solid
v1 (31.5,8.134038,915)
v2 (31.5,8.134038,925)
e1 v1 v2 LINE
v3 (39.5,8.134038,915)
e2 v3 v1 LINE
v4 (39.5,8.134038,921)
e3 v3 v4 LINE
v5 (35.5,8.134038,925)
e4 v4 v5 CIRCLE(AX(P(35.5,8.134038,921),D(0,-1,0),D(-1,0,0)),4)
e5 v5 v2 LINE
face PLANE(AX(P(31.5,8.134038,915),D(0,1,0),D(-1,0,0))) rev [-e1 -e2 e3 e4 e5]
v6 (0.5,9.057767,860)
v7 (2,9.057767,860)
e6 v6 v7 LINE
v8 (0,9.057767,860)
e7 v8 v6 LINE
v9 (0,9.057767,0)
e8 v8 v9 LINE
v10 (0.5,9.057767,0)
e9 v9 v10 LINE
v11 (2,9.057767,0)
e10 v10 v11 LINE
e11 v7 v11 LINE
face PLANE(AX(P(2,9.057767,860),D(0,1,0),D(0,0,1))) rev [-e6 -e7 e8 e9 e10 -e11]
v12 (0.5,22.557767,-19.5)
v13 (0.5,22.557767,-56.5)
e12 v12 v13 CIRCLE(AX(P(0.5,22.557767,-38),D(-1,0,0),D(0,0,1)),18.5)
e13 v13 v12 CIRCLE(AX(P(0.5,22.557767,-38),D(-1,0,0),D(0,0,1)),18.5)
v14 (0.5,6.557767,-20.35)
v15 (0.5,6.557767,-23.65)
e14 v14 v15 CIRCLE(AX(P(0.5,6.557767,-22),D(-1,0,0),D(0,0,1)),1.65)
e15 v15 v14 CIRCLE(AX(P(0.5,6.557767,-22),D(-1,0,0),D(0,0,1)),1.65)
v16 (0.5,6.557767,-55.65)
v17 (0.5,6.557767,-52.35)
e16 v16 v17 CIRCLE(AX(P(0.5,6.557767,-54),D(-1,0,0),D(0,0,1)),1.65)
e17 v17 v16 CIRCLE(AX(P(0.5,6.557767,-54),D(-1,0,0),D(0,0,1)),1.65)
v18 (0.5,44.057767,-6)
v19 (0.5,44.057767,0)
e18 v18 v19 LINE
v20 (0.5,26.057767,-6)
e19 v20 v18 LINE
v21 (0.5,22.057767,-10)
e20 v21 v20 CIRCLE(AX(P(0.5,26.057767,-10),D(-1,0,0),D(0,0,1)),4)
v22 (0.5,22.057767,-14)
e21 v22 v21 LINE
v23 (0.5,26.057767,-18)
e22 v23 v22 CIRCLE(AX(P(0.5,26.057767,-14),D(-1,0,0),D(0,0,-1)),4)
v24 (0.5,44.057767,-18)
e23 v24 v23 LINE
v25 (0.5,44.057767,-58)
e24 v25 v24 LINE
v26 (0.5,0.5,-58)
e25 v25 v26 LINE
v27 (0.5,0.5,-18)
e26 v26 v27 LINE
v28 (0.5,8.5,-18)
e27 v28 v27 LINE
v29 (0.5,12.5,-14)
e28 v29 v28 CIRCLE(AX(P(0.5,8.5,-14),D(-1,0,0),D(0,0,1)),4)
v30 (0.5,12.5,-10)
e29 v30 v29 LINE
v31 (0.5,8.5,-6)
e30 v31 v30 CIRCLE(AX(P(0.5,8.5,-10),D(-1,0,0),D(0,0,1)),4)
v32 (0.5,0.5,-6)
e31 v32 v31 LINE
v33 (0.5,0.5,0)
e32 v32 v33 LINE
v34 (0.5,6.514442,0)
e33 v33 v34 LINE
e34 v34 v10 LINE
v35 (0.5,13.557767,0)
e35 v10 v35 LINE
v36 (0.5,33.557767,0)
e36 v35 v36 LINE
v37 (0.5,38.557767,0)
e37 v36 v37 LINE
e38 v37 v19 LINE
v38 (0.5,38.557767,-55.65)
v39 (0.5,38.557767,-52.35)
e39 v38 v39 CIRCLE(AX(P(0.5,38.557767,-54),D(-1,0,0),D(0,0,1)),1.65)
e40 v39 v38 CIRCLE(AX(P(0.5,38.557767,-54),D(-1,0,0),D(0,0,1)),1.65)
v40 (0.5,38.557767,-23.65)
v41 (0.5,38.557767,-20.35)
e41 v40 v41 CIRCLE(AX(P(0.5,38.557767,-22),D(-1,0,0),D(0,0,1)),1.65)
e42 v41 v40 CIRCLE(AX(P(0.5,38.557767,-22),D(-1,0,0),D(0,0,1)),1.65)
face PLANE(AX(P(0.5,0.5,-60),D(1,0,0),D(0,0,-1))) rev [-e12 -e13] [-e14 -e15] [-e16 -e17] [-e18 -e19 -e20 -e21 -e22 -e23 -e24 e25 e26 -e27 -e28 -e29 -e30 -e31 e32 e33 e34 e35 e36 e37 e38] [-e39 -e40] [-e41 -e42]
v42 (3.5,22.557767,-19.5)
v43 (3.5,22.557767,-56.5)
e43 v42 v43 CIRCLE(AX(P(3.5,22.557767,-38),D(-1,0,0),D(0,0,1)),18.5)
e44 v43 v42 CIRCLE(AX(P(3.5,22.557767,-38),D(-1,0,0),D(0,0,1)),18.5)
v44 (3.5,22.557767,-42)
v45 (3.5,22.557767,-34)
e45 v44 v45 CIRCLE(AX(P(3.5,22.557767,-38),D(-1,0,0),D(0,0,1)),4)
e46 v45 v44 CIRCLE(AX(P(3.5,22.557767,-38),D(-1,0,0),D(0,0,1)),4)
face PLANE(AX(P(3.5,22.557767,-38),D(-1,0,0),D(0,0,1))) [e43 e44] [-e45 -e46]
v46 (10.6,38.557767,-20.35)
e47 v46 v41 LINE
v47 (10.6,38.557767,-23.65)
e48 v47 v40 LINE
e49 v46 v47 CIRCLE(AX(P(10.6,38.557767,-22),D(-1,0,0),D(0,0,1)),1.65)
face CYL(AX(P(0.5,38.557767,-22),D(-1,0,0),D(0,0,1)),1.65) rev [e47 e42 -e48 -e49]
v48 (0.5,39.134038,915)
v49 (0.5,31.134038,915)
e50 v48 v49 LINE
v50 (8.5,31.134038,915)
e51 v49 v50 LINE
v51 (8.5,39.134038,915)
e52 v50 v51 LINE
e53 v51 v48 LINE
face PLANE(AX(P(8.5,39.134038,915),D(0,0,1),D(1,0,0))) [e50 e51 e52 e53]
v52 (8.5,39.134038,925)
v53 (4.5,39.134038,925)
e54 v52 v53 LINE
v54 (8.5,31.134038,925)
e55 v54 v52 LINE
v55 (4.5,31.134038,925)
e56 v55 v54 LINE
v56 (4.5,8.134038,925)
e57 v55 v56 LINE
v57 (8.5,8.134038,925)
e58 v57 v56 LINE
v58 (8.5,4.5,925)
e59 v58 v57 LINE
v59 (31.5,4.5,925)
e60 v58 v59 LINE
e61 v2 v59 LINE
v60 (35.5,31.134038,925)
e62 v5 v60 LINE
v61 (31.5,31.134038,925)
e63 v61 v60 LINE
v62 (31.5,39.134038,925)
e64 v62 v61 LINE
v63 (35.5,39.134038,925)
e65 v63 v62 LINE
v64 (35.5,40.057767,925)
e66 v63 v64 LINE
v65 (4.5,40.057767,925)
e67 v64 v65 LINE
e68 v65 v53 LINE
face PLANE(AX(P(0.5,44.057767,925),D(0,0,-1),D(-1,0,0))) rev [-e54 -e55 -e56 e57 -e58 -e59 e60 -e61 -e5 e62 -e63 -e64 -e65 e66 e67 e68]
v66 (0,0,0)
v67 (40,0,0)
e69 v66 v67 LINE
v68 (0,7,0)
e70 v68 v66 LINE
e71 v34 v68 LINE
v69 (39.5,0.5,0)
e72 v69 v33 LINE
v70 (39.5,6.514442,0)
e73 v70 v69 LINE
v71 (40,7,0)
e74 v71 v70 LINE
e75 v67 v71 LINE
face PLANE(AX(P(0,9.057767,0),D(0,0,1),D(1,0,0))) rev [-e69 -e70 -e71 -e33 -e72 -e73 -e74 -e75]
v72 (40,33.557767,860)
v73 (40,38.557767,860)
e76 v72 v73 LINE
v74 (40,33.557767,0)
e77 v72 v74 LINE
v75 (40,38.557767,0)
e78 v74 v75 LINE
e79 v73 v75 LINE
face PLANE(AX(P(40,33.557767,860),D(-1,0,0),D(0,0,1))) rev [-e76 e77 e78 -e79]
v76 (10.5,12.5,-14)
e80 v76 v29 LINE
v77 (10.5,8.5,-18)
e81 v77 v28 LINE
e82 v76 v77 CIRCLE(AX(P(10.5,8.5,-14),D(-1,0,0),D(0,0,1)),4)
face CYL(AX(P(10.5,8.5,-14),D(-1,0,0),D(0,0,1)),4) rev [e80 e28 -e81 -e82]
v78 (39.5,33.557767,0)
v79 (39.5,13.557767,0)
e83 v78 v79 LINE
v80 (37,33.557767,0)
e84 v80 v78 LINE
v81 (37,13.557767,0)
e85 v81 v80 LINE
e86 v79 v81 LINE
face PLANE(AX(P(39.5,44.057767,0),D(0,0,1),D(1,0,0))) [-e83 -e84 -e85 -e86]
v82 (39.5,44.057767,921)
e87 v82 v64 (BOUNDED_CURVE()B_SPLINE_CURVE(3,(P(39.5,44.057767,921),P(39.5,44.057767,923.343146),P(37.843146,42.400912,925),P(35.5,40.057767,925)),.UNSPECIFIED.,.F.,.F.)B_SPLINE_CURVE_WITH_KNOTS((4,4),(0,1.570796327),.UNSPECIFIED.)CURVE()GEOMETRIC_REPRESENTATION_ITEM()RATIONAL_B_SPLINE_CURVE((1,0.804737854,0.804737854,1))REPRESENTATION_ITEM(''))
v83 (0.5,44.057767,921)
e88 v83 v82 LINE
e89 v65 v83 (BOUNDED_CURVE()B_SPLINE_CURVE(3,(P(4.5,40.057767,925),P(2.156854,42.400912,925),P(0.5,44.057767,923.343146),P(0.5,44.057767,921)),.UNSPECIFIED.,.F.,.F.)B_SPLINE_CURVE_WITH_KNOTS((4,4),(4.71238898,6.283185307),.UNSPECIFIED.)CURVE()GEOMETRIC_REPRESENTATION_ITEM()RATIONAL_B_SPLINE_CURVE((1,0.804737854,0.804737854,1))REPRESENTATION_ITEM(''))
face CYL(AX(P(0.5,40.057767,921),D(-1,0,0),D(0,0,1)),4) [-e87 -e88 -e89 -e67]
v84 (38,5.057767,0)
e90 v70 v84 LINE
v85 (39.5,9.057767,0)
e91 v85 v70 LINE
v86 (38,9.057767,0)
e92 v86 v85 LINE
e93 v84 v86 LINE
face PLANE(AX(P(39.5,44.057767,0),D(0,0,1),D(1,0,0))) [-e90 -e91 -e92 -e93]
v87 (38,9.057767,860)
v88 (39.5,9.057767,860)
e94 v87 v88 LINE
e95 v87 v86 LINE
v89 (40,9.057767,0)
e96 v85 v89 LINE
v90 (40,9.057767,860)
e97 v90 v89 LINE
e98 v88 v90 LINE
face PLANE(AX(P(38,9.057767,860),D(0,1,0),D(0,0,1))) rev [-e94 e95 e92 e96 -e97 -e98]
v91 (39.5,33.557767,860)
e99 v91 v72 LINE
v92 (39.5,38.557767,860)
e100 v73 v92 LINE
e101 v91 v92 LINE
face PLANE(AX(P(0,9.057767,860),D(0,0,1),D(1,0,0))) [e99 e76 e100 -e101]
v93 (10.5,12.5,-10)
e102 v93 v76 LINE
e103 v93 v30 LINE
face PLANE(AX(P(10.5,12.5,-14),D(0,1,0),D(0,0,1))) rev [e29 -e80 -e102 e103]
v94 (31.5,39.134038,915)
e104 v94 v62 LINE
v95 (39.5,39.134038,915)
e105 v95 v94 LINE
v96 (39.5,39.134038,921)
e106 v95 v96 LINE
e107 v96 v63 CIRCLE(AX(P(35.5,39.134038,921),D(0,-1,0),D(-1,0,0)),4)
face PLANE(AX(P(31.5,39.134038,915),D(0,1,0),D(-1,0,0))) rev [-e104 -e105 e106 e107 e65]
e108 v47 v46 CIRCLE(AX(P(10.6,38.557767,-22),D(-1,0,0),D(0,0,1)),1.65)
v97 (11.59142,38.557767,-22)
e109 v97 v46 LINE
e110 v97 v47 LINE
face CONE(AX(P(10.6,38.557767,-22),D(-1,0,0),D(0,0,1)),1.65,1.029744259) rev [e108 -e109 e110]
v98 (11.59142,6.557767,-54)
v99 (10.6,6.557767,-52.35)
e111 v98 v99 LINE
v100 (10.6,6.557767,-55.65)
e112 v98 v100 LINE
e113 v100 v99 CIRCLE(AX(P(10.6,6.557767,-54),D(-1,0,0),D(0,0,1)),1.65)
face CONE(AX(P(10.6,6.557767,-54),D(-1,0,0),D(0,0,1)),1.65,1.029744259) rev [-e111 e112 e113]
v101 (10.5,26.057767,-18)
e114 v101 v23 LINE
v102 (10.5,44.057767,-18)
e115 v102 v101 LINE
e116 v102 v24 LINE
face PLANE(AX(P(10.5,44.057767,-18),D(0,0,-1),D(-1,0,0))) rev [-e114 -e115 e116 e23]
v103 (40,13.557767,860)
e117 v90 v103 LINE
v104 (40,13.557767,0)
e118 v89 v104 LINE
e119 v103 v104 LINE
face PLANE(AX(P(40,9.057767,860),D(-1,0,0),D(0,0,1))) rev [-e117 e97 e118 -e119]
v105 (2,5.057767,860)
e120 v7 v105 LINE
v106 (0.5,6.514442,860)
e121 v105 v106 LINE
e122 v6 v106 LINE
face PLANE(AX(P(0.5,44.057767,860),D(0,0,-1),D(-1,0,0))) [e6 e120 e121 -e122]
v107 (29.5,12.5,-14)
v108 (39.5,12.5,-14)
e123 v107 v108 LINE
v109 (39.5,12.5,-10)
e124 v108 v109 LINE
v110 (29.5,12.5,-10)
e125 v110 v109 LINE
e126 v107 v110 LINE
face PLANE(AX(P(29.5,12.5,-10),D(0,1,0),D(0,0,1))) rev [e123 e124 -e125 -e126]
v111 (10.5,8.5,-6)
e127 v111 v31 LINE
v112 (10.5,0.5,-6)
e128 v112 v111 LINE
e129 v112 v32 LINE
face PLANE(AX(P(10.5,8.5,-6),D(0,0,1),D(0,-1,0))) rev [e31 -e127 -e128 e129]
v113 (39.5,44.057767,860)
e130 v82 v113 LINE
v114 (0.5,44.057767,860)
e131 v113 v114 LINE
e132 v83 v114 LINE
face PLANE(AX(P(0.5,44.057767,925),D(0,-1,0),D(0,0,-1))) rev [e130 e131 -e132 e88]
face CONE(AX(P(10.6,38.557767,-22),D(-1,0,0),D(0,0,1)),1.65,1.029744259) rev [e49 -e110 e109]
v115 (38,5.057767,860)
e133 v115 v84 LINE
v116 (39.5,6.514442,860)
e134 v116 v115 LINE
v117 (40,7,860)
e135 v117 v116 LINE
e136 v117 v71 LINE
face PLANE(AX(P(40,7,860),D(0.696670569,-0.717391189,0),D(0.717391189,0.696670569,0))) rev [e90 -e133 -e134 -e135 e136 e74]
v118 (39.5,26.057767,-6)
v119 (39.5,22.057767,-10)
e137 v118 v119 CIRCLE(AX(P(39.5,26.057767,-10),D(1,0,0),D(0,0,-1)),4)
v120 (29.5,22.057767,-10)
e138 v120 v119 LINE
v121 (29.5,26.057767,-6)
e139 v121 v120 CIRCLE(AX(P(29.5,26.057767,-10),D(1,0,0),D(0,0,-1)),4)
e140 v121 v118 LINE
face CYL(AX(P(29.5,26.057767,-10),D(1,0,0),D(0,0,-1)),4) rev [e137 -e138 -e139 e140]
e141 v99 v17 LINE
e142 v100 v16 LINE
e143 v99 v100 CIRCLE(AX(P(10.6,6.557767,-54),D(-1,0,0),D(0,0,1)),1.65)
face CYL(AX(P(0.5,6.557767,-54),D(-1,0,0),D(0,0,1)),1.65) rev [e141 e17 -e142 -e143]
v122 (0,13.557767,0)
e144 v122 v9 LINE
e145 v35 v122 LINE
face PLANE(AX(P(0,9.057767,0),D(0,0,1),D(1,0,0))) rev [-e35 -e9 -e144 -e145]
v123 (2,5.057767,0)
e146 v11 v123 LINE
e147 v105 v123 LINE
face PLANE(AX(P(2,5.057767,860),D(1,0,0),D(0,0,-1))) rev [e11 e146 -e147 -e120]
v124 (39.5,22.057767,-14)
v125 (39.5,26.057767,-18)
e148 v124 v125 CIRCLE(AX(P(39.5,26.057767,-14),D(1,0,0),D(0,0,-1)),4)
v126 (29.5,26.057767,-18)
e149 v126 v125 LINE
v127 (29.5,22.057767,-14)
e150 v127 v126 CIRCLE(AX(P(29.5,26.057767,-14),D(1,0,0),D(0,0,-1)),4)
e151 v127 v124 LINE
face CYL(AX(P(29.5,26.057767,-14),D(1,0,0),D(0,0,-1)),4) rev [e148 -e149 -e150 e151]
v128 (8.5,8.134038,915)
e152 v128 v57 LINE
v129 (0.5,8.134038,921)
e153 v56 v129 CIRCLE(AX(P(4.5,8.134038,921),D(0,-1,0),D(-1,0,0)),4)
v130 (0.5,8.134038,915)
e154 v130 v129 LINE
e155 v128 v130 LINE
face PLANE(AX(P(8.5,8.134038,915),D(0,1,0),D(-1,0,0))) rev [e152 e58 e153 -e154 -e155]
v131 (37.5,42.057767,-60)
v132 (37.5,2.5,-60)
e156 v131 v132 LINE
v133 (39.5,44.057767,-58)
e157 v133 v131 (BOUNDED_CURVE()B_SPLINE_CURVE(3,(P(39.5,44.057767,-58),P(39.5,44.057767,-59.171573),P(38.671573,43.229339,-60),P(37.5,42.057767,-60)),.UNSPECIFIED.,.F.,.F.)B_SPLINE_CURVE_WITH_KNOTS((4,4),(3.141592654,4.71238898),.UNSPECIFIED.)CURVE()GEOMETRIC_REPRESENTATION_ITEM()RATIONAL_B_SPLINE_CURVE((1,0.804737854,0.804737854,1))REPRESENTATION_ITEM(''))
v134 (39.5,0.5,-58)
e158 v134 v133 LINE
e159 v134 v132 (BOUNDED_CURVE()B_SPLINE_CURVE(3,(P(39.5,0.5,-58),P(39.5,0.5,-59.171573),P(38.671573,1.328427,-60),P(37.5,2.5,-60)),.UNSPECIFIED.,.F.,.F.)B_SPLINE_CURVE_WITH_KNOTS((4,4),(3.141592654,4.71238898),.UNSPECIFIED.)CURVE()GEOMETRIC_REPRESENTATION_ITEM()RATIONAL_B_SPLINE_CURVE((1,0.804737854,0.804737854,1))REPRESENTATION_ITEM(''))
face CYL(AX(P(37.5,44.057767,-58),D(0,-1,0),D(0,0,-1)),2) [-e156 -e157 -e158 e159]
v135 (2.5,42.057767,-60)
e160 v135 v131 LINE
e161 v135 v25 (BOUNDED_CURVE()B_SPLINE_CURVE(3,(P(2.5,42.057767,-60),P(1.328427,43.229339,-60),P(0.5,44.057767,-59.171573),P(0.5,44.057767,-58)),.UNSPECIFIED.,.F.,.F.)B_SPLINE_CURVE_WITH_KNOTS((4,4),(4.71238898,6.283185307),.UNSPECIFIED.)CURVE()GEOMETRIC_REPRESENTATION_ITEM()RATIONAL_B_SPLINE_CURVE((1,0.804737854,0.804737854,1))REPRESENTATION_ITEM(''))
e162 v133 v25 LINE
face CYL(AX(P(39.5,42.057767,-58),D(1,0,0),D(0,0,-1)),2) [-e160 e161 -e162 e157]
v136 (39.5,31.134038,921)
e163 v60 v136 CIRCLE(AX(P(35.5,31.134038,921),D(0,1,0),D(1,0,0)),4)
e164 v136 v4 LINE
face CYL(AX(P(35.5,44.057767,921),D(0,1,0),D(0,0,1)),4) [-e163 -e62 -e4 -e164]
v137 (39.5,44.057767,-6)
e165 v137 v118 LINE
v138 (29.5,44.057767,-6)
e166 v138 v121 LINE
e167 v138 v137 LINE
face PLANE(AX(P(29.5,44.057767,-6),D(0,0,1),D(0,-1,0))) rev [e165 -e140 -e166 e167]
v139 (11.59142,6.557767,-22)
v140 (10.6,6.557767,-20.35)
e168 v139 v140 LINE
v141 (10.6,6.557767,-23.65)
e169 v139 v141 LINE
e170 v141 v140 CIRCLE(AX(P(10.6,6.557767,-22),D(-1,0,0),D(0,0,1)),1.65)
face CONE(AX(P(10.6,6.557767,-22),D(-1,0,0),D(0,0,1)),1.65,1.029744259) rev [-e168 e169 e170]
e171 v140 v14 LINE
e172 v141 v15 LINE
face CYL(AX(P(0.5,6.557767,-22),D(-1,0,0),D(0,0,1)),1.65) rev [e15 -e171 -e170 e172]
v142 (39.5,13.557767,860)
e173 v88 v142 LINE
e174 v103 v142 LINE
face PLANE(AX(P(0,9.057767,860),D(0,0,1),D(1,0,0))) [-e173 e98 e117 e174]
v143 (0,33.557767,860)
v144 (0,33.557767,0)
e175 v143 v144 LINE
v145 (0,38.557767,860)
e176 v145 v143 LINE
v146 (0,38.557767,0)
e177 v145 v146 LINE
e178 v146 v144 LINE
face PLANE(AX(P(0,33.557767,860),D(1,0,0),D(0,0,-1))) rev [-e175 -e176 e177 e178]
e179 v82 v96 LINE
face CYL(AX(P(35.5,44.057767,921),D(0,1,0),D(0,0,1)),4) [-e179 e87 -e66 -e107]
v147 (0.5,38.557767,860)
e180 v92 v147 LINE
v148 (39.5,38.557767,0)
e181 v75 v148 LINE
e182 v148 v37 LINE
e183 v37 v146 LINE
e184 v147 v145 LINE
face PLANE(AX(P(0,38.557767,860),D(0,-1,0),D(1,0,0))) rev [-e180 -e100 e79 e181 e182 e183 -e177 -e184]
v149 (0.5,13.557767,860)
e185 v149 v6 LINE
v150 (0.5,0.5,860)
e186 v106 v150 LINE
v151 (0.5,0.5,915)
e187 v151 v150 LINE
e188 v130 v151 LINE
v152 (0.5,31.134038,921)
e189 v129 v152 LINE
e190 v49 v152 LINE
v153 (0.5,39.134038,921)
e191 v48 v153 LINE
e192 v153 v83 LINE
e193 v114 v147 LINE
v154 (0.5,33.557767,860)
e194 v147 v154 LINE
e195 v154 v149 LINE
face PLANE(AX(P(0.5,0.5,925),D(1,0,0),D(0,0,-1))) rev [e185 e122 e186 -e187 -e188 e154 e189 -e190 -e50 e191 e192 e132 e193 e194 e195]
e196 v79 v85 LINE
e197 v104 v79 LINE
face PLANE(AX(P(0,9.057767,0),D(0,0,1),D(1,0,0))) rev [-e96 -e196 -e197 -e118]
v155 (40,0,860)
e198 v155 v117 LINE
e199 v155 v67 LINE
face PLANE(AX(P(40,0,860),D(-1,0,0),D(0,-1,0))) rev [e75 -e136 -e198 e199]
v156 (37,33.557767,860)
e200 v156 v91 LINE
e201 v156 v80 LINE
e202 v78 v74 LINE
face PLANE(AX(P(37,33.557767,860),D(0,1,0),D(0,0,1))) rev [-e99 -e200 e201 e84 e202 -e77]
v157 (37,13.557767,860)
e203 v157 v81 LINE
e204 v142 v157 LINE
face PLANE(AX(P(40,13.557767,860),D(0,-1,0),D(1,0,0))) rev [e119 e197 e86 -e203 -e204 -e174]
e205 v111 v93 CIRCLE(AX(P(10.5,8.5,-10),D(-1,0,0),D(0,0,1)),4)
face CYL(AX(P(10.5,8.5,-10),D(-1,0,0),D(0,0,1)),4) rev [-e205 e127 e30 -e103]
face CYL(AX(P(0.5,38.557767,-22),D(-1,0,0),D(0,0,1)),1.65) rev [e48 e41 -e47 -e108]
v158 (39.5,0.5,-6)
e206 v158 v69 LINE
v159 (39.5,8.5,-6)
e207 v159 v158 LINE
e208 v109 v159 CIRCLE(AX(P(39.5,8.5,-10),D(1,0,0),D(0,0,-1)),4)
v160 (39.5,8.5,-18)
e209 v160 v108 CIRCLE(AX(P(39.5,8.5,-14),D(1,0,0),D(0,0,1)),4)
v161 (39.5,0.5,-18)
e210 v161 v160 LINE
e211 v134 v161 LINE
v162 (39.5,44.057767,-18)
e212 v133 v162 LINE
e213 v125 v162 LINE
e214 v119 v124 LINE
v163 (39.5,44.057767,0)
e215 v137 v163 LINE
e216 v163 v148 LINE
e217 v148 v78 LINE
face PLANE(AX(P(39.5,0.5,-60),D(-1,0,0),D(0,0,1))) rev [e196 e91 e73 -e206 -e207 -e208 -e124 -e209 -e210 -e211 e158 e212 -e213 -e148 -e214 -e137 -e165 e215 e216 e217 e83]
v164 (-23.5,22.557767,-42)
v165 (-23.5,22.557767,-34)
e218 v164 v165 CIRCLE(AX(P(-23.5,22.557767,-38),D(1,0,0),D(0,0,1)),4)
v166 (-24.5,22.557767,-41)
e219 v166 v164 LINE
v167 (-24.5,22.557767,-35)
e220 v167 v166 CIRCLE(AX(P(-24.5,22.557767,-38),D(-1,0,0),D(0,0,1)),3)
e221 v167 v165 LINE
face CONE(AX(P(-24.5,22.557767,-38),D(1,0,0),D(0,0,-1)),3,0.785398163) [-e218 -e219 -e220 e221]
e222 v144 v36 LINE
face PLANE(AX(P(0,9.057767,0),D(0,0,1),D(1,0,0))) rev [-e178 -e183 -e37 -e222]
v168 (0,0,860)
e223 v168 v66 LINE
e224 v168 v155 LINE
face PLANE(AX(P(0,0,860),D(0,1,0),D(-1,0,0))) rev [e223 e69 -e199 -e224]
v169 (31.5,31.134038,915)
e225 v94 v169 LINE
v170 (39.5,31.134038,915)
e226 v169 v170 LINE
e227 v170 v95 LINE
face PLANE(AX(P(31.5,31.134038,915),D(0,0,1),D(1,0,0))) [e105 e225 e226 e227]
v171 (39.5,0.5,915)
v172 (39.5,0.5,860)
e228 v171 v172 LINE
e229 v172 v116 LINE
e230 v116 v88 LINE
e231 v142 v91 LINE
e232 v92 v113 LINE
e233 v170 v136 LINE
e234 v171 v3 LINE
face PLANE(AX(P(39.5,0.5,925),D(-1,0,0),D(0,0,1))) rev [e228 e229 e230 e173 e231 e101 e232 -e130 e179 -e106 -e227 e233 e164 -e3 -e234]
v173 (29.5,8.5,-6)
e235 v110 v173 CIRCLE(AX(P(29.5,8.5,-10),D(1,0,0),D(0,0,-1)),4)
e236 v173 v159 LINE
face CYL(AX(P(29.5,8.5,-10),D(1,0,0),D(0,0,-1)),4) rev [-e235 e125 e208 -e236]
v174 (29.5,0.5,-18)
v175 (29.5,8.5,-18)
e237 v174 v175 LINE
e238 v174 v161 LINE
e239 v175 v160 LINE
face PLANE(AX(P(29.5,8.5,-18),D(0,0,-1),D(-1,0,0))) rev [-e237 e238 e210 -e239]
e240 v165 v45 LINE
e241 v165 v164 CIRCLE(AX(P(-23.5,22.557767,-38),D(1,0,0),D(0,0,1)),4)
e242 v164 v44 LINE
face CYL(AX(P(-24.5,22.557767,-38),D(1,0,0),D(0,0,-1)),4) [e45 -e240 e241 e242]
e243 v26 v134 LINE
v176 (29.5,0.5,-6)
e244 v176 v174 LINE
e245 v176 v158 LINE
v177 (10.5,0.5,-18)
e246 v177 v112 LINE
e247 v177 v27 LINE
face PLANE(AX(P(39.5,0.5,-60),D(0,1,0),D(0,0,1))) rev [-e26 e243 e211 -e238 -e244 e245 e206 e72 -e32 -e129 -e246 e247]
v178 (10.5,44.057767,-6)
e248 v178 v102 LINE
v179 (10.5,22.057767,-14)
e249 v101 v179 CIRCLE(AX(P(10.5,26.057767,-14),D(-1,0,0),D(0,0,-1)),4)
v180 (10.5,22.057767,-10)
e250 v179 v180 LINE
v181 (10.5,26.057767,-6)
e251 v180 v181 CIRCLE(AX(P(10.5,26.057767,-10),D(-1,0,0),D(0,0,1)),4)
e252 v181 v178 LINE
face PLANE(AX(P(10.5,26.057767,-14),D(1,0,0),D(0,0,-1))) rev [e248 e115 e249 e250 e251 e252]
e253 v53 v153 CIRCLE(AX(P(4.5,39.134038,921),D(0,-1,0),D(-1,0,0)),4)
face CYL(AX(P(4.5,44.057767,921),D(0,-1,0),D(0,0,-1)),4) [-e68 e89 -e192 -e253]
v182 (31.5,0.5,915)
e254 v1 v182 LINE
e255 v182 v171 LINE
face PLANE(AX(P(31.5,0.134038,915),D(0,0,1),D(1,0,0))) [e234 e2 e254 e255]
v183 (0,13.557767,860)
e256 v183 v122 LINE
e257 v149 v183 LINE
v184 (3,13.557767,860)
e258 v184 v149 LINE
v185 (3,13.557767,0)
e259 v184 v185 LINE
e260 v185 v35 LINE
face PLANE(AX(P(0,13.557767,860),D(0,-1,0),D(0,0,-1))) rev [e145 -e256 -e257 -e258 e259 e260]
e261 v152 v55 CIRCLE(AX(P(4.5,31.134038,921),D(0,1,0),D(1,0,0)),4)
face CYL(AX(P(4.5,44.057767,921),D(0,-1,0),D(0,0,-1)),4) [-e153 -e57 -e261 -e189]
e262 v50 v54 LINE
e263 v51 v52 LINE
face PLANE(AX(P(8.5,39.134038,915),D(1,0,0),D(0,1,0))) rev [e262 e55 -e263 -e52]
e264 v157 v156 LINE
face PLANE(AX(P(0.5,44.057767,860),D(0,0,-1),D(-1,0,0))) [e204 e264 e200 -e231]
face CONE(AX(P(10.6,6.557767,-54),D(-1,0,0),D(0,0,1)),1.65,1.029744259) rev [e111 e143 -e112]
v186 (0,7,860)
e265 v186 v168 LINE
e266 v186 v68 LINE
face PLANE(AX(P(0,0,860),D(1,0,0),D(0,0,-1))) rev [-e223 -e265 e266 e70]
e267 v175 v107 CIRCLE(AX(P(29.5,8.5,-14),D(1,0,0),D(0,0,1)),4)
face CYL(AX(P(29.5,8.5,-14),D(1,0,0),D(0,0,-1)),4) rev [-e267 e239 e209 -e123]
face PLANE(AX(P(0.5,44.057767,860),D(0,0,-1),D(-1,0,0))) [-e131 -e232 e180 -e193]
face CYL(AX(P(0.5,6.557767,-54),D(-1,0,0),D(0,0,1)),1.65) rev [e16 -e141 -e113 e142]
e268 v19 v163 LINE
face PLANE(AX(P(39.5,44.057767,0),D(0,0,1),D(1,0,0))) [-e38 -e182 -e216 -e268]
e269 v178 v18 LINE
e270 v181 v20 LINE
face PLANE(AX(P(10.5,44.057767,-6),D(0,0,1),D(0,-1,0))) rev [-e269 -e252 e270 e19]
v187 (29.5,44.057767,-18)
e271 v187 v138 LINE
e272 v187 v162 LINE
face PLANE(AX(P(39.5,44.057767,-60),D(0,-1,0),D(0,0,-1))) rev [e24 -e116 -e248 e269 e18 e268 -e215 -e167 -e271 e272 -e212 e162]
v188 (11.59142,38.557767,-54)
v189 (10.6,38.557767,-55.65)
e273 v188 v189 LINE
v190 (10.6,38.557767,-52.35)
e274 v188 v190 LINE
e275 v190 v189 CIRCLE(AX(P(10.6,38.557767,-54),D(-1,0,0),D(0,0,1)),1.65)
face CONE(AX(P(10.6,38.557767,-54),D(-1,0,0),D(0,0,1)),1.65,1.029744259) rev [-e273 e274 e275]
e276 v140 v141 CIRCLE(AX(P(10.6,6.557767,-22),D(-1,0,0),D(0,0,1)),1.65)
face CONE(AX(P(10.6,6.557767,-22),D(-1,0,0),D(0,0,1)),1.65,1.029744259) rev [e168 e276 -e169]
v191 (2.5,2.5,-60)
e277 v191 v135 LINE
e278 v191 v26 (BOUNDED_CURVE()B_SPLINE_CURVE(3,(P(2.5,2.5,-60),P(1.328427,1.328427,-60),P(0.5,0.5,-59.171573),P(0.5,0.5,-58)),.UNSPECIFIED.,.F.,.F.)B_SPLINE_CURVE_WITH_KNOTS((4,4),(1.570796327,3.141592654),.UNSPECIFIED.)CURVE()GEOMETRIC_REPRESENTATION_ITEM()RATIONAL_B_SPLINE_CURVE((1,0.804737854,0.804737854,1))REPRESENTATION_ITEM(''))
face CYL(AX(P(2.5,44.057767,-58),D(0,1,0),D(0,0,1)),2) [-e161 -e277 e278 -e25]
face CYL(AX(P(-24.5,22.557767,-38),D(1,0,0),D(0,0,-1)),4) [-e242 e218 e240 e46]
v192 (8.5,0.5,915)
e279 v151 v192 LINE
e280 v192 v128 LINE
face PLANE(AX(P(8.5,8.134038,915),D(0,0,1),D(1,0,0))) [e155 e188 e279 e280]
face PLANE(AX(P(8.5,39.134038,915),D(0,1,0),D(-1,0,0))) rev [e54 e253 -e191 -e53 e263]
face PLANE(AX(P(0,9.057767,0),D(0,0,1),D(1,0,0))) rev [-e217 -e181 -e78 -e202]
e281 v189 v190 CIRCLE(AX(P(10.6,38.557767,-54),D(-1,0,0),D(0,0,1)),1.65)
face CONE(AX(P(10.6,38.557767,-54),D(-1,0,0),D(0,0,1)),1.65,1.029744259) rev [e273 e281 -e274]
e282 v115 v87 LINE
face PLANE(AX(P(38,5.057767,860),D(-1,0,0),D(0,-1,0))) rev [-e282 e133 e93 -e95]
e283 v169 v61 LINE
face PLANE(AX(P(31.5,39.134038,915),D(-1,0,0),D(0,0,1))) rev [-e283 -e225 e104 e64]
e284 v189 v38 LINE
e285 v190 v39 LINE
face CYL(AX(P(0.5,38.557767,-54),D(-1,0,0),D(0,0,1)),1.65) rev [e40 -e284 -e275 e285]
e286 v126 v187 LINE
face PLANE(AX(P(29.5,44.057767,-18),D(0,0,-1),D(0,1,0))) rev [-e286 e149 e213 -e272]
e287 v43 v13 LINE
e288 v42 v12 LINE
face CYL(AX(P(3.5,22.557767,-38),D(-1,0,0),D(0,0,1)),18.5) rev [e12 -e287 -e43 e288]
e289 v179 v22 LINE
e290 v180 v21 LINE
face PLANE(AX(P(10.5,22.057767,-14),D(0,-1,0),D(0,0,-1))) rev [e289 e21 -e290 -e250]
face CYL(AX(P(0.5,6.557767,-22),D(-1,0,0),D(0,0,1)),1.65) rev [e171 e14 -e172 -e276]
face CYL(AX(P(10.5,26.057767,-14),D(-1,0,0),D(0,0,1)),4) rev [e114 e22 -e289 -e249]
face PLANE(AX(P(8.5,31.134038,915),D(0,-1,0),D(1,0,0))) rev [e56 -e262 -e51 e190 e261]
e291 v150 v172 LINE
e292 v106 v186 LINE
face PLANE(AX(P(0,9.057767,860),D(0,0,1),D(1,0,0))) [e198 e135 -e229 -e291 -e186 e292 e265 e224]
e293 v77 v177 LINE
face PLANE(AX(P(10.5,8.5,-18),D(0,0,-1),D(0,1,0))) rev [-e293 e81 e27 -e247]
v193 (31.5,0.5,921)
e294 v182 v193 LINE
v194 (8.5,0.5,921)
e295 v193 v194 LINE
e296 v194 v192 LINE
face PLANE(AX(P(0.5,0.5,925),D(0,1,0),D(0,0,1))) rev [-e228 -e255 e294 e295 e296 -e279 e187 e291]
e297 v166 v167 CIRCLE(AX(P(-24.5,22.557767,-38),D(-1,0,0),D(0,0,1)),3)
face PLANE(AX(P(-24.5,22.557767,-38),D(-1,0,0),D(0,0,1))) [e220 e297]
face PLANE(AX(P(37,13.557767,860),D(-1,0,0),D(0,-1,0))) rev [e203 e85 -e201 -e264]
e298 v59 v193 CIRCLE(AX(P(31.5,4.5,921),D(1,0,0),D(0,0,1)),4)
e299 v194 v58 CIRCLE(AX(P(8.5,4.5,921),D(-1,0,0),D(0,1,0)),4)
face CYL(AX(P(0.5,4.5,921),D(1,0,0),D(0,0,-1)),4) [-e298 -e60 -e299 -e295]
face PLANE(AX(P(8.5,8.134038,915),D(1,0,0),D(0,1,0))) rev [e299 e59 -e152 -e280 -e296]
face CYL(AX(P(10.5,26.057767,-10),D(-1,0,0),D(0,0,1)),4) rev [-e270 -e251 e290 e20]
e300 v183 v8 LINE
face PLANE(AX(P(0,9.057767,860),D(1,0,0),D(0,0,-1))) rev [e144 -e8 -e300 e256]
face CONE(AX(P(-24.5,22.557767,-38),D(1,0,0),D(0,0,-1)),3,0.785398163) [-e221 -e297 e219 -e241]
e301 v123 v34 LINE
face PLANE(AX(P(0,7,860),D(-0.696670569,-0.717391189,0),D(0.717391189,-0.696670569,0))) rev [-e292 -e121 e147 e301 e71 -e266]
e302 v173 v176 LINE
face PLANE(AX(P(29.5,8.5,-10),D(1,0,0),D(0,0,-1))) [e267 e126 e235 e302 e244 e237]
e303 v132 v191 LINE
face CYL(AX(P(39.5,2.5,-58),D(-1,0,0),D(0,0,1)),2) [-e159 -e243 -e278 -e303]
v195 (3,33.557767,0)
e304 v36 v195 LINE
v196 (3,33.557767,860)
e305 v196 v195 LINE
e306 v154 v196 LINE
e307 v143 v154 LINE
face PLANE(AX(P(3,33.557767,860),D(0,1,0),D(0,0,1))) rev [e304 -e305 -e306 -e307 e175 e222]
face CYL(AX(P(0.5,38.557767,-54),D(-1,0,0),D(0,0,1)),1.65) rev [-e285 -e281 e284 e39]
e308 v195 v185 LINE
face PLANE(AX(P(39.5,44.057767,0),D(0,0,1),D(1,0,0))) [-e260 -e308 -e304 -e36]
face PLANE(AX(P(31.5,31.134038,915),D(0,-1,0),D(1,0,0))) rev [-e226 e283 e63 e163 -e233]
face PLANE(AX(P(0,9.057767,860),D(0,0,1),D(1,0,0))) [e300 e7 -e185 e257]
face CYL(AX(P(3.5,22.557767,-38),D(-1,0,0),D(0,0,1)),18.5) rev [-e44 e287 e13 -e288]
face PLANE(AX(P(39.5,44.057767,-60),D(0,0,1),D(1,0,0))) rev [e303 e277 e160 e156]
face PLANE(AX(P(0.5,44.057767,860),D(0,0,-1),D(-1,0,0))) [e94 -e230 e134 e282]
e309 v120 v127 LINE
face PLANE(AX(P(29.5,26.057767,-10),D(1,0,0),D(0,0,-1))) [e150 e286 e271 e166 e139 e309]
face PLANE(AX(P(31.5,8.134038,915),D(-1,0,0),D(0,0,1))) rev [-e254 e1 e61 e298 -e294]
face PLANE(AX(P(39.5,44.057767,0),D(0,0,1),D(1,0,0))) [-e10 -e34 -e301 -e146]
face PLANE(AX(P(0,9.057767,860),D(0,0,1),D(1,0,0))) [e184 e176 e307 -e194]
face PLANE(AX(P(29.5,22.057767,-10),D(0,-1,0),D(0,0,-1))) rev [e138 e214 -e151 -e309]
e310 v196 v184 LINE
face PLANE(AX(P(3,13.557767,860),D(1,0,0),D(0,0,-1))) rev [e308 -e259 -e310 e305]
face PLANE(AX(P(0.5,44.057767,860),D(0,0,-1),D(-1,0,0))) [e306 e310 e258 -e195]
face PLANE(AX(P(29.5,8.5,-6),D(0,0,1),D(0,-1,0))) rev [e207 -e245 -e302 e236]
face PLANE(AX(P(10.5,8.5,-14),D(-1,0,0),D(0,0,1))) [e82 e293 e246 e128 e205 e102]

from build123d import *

# Parameters (mm, degrees)
EXTRUDE_473_DEPTH      = 860
SKETCH_2_W             = 39
SKETCH_2_H             = 43.557766586
EXTRUDE_1_DEPTH        = 65
FILLET_2_R             = 4
SKETCH_3_W             = 8
SKETCH_3_H             = 8
CUT_EXTRUDE_1_DEPTH    = 10
SKETCH_4_W             = 39
SKETCH_4_H             = 43.557766586
EXTRUDE_3_DEPTH        = 60
FILLET_4_R             = 2
CUT_EXTRUDE_2_DEPTH    = 10
CUT_EXTRUDE_START      = -10
CUT_EXTRUDE_3_DEPTH    = 10
HOLE_WIZARD_M4_1_D     = 3.3
HOLE_WIZARD_M4_1_DEPTH = 10.1
HOLE_WIZARD_M4_1_TIP   = 0.991420021
SKETCH_13_R            = 18.5
CUT_EXTRUDE_4_DEPTH    = 3
SKETCH_14_R            = 4
EXTRUDE_5_DEPTH        = 28
CHAMFER_1_SIZE         = 1


with BuildPart() as part:
    # 草图1 → Extrude 473 (new body)
    with BuildSketch(Plane.XY):
        Polygon((0, 0), (40, 0), (40, 7), (38, 5.057766586), (38, 9.057766586), (40, 9.057766586), (40, 13.557766586), (37, 13.557766586), (37, 33.557766586), (40, 33.557766586), (40, 38.557766586), (0, 38.557766586), (0, 33.557766586), (3, 33.557766586), (3, 13.557766586), (0, 13.557766586), (0, 9.057766586), (2, 9.057766586), (2, 5.057766586), (0, 7), align=None)
    extrude(amount=EXTRUDE_473_DEPTH)

    # 草图2 → 凸台-拉伸1 (add)
    with BuildSketch(Plane.XY.offset(860)):
        with Locations((20, 22.278883293)):
            Rectangle(SKETCH_2_W, SKETCH_2_H)
    extrude(amount=EXTRUDE_1_DEPTH)

    # 圆角2
    fillet_2_edges = [part.edges().sort_by_distance(p)[0] for p in [
        (0.5, 22.278883293, 925),
        (20, 0.5, 925),
        (39.5, 22.278883293, 925),
        (20, 44.057766586, 925),
    ]]
    fillet(fillet_2_edges, radius=FILLET_2_R)

    # 草图3 → 切除-拉伸1 (cut)
    with BuildSketch(Plane.XY.offset(925)):
        with Locations((4.5, 35.134037638)):
            Rectangle(SKETCH_3_W, SKETCH_3_H)
        with Locations((35.5, 4.134037638)):
            Rectangle(SKETCH_3_W, SKETCH_3_H)
        with Locations((35.5, 35.134037638)):
            Rectangle(SKETCH_3_W, SKETCH_3_H)
        with Locations((4.5, 4.134037638)):
            Rectangle(SKETCH_3_W, SKETCH_3_H)
    extrude(amount=-CUT_EXTRUDE_1_DEPTH, mode=Mode.SUBTRACT)

    # 草图4 → 凸台-拉伸3 (add)
    with BuildSketch(Plane(origin=(0, 0, 0), x_dir=(-1, 0, 0), z_dir=(0, 0, -1))):
        with Locations((-20, 22.278883293)):
            Rectangle(SKETCH_4_W, SKETCH_4_H)
    extrude(amount=EXTRUDE_3_DEPTH)

    # 圆角4
    fillet_4_edges = [part.edges().sort_by_distance(p)[0] for p in [
        (39.5, 22.278883293, -60),
        (20, 0.5, -60),
        (0.5, 22.278883293, -60),
        (20, 44.057766586, -60),
    ]]
    fillet(fillet_4_edges, radius=FILLET_4_R)

    # 草图5 → 切除-拉伸2 (cut)
    with BuildSketch(Plane.ZY.offset(-0.5)):
        with BuildLine():
            Line((-18, 44.057766586), (-6, 44.057766586))
            Line((-6, 44.057766586), (-6, 26.057766586))
            ThreePointArc((-6, 26.057766586), (-7.171572875, 23.229339461), (-10, 22.057766586))
            Line((-10, 22.057766586), (-14, 22.057766586))
            ThreePointArc((-14, 22.057766586), (-16.828427125, 23.229339461), (-18, 26.057766586))
            Line((-18, 26.057766586), (-18, 44.057766586))
        make_face()
        with BuildLine():
            Line((-14, 12.5), (-10, 12.5))
            ThreePointArc((-10, 12.5), (-7.171572875, 11.328427125), (-6, 8.5))
            Line((-6, 8.5), (-6, 0.5))
            Line((-6, 0.5), (-18, 0.5))
            Line((-18, 0.5), (-18, 8.5))
            ThreePointArc((-18, 8.5), (-16.828427125, 11.328427125), (-14, 12.5))
        make_face()
    extrude(amount=-CUT_EXTRUDE_2_DEPTH, mode=Mode.SUBTRACT)

    # 草图7 → 切除-拉伸3 (cut)
    with BuildSketch(Plane(origin=(39.5, 0, 0), x_dir=(0, 0, -1), z_dir=(1, 0, 0)).offset(CUT_EXTRUDE_START)):
        with BuildLine():
            Line((6, 44.057766586), (18, 44.057766586))
            Line((18, 44.057766586), (18, 26.057766586))
            ThreePointArc((18, 26.057766586), (16.828427125, 23.229339461), (14, 22.057766586))
            Line((14, 22.057766586), (10, 22.057766586))
            ThreePointArc((10, 22.057766586), (7.171572875, 23.229339461), (6, 26.057766586))
            Line((6, 26.057766586), (6, 44.057766586))
        make_face()
        with BuildLine():
            Line((10, 12.5), (14, 12.5))
            ThreePointArc((14, 12.5), (16.828427125, 11.328427125), (18, 8.5))
            Line((18, 8.5), (18, 0.5))
            Line((18, 0.5), (6, 0.5))
            Line((6, 0.5), (6, 8.5))
            ThreePointArc((6, 8.5), (7.171572875, 11.328427125), (10, 12.5))
        make_face()
    extrude(amount=CUT_EXTRUDE_3_DEPTH, mode=Mode.SUBTRACT)

    # M4 螺纹孔1
    with Locations(Plane.ZY.offset(-0.5)):
        with Locations((-22, 6.557766586), (-54, 6.557766586), (-22, 38.557766586), (-54, 38.557766586)):
            Hole(HOLE_WIZARD_M4_1_D / 2, depth=HOLE_WIZARD_M4_1_DEPTH)
            with Locations((0, 0, -(HOLE_WIZARD_M4_1_DEPTH + HOLE_WIZARD_M4_1_TIP / 2))):  # 118° drill point
                Cone(0, HOLE_WIZARD_M4_1_D / 2, HOLE_WIZARD_M4_1_TIP, mode=Mode.SUBTRACT)

    # 草图13 → 切除-拉伸4 (cut)
    with BuildSketch(Plane.ZY.offset(-0.5)):
        with Locations((-38, 22.557766586)):
            Circle(SKETCH_13_R)
    extrude(amount=-CUT_EXTRUDE_4_DEPTH, mode=Mode.SUBTRACT)

    # 草图14 → 凸台-拉伸5 (add)
    with BuildSketch(Plane.ZY.offset(-3.5)):
        with Locations((-38, 22.557766586)):
            Circle(SKETCH_14_R)
    extrude(amount=EXTRUDE_5_DEPTH)

    # 倒角1
    chamfer_1_edges = [part.edges().sort_by_distance(p)[0] for p in [
        (-24.5, 22.557766586, -42),
    ]]
    chamfer(chamfer_1_edges, length=CHAMFER_1_SIZE)


solid = part.part
